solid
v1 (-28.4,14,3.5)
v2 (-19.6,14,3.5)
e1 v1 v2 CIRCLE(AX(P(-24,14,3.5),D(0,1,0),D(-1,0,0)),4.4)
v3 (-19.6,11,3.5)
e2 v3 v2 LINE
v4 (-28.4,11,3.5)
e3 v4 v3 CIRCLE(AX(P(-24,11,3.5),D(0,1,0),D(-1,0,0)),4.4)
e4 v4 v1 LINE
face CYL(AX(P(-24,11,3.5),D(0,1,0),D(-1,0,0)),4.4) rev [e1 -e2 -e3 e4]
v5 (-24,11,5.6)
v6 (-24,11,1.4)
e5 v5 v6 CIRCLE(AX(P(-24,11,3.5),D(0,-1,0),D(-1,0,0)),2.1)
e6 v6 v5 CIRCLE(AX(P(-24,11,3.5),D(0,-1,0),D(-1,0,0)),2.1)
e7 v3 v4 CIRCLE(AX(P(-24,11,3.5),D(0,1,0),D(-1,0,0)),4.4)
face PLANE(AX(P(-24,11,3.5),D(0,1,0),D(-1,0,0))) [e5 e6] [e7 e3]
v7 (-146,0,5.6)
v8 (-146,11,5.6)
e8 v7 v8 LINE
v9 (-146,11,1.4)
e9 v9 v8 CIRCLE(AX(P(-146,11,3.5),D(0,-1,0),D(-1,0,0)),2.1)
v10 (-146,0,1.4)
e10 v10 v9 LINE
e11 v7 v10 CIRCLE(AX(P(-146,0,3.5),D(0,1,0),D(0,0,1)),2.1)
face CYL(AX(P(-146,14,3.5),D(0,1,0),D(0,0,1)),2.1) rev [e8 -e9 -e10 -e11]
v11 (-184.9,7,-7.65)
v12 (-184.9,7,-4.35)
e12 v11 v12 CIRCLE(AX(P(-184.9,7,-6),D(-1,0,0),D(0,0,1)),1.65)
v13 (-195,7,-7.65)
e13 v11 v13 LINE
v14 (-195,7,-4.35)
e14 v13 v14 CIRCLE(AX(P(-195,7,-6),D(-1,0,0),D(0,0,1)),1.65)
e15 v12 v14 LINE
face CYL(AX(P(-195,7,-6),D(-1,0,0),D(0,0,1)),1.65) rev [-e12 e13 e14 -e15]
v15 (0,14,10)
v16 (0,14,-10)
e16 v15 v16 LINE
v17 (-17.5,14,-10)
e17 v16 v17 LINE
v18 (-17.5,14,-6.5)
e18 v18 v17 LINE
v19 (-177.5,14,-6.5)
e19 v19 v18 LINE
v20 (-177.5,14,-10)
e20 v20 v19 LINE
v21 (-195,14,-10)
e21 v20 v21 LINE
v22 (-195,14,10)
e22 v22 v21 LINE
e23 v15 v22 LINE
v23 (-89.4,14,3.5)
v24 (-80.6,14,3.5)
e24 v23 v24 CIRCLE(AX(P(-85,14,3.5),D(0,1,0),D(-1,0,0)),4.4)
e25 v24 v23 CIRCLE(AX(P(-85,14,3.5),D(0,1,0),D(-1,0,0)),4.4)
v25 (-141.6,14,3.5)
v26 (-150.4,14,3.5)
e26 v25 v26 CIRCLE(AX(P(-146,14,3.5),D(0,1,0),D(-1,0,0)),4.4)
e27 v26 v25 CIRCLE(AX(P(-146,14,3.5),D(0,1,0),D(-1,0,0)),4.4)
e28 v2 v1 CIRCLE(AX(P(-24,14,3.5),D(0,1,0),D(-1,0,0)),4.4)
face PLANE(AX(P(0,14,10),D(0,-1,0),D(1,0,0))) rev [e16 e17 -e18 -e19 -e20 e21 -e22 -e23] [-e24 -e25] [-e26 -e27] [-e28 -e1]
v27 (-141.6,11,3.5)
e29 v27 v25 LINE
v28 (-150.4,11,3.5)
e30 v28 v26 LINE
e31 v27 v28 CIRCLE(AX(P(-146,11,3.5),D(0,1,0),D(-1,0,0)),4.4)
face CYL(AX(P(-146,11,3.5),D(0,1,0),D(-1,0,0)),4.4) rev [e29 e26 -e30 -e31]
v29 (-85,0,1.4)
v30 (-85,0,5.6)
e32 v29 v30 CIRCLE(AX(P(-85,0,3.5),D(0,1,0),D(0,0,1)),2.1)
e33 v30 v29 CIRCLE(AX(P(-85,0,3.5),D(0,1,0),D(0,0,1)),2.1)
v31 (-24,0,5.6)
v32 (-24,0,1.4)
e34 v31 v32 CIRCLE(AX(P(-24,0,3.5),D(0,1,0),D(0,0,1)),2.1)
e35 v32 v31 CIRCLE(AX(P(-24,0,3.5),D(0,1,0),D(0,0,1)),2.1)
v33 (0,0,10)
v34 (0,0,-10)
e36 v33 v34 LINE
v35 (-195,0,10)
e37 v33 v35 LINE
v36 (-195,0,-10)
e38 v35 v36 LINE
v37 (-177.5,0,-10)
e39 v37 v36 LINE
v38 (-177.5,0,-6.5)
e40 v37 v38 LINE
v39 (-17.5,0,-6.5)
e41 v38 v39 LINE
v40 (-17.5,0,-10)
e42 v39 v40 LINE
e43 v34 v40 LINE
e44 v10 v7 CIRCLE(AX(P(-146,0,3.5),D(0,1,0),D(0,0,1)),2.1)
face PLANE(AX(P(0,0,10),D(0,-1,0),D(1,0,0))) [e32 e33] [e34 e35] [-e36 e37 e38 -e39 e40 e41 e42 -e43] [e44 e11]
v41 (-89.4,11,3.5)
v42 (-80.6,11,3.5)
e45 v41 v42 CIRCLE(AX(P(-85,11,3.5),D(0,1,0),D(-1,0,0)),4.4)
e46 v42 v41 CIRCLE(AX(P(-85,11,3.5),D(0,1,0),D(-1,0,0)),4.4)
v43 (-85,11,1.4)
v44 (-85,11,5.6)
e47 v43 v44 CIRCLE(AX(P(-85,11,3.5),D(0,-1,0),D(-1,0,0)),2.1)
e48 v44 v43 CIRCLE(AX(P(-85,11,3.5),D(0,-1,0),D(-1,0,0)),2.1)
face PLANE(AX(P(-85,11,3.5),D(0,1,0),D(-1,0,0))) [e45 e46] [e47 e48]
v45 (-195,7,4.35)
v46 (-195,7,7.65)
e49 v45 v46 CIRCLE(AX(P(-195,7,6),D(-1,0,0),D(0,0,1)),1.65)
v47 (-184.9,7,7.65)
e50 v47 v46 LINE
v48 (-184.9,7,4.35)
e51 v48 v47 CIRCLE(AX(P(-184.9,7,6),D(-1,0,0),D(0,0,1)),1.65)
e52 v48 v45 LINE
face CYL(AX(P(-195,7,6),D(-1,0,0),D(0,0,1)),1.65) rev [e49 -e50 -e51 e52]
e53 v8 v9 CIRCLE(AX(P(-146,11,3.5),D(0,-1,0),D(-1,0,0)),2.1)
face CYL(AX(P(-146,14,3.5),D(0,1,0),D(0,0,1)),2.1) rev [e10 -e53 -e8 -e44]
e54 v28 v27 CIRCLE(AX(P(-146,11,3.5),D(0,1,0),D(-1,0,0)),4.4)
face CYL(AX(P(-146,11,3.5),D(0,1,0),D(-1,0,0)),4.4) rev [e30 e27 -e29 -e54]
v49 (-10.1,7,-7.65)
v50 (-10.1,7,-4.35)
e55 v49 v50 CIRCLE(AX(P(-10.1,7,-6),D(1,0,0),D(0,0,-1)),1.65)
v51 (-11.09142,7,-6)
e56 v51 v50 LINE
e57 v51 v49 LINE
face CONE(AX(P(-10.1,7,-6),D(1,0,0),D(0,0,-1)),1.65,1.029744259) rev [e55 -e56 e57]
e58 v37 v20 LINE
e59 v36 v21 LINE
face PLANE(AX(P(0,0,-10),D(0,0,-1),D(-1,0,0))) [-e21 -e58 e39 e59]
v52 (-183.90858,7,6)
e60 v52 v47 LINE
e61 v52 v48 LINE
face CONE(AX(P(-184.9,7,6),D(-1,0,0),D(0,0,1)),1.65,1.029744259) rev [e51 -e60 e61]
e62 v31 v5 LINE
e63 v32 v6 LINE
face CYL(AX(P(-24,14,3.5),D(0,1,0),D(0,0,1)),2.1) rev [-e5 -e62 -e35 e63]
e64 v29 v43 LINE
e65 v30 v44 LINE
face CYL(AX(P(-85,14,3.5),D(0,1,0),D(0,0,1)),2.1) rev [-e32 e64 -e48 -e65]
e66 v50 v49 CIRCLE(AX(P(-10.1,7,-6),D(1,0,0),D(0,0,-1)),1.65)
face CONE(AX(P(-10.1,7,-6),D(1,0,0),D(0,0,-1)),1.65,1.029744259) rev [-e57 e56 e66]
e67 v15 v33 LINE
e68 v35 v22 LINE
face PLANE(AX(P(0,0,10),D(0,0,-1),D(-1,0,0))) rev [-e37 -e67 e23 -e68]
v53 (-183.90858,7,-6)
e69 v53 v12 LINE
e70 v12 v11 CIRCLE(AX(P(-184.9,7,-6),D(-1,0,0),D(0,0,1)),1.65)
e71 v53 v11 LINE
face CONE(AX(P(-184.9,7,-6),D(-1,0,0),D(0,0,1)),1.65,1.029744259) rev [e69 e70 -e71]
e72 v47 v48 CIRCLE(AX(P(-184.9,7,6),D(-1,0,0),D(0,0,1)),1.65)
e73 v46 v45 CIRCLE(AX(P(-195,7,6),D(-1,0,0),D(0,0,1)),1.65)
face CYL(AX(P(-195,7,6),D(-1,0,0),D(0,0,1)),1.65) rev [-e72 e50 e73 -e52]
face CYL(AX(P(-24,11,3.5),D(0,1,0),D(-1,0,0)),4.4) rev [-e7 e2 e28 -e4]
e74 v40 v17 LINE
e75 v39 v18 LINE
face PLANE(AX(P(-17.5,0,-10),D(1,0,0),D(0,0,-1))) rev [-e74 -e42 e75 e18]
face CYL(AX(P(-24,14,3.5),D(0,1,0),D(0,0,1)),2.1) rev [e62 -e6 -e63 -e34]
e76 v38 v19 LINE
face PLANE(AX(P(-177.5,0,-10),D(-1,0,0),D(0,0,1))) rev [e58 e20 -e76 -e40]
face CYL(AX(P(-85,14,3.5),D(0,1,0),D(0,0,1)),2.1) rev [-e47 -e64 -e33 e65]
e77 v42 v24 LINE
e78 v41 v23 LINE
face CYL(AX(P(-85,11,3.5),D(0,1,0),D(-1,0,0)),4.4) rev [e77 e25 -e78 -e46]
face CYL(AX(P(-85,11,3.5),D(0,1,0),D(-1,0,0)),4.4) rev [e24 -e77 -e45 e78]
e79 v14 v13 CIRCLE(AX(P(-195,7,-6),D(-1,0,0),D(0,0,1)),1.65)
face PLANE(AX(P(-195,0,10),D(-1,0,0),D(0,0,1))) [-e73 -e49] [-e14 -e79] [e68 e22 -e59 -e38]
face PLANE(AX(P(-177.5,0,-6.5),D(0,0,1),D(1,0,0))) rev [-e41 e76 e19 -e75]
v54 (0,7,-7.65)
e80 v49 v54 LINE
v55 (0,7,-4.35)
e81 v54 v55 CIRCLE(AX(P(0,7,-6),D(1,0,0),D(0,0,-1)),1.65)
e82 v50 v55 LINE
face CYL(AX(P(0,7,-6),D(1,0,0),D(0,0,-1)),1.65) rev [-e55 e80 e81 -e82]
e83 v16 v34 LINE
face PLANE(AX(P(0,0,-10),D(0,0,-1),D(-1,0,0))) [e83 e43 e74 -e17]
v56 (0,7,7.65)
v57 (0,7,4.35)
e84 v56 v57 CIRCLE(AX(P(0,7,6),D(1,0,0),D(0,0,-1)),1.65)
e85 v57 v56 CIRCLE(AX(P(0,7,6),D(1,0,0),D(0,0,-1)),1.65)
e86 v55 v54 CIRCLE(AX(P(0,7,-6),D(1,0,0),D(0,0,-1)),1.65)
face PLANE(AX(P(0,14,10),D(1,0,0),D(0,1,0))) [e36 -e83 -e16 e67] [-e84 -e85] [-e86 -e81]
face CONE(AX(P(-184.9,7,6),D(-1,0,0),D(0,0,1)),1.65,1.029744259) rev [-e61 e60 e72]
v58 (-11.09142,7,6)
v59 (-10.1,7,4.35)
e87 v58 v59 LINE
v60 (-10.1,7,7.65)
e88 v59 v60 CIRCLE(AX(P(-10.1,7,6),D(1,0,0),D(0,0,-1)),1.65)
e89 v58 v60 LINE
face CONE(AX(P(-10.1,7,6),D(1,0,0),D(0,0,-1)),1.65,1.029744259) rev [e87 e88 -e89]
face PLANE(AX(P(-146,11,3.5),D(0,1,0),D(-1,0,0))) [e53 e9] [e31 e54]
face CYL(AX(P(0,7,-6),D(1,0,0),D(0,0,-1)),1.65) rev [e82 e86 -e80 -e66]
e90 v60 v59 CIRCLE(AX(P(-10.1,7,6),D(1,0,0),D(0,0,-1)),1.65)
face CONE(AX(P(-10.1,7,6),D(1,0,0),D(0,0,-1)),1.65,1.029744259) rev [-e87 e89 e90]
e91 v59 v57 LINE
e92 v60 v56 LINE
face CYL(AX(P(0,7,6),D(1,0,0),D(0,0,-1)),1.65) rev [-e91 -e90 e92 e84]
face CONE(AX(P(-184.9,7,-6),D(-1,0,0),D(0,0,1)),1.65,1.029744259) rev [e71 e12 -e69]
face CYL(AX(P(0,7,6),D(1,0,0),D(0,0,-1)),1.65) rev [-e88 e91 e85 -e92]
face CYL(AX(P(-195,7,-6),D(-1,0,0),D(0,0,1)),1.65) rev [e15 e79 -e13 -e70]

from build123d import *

# Parameters (mm, degrees)
SKETCH1_W             = 195
SKETCH1_H             = 14
EXTRUDE_THIN1_DEPTH   = 10
M4_TAPPED_HOLE1_D     = 3.3
M4_TAPPED_HOLE1_DEPTH = 10.1
M4_TAPPED_HOLE1_TIP   = 0.991420021
M4_TAPPED_HOLE2_D     = 3.3
M4_TAPPED_HOLE2_DEPTH = 10.1
M4_TAPPED_HOLE2_TIP   = 0.991420021
M5_TAPPED_HOLE1_D     = 4.2
SKETCH9_R             = 4.4
CUT_EXTRUDE1_DEPTH    = 3
SKETCH10_W            = 160
SKETCH10_H            = 3.5
CUT_EXTRUDE2_DEPTH    = 196.757503049


with BuildPart() as part:
    # Sketch1 → Extrude-Thin1 (new, symmetric)
    with BuildSketch(Plane.XY):
        with Locations((-97.5, 7)):
            Rectangle(SKETCH1_W, SKETCH1_H)
    extrude(amount=EXTRUDE_THIN1_DEPTH, both=True)

    # M4 Tapped Hole1
    with Locations(Plane.ZY.offset(195)):
        with Locations((-6, 7), (6, 7)):
            Hole(M4_TAPPED_HOLE1_D / 2, depth=M4_TAPPED_HOLE1_DEPTH)
            with Locations((0, 0, -(M4_TAPPED_HOLE1_DEPTH + M4_TAPPED_HOLE1_TIP / 2))):  # 118° drill point
                Cone(0, M4_TAPPED_HOLE1_D / 2, M4_TAPPED_HOLE1_TIP, mode=Mode.SUBTRACT)

    # M4 Tapped Hole2
    with Locations(Plane(origin=(0, 0, 0), x_dir=(0, 0, -1), z_dir=(1, 0, 0))):
        with Locations((-6, 7), (6, 7)):
            Hole(M4_TAPPED_HOLE2_D / 2, depth=M4_TAPPED_HOLE2_DEPTH)
            with Locations((0, 0, -(M4_TAPPED_HOLE2_DEPTH + M4_TAPPED_HOLE2_TIP / 2))):  # 118° drill point
                Cone(0, M4_TAPPED_HOLE2_D / 2, M4_TAPPED_HOLE2_TIP, mode=Mode.SUBTRACT)

    # M5 Tapped Hole1 (through all)
    with Locations(Plane(origin=(0, 14, 0), x_dir=(1, 0, 0), z_dir=(0, 1, 0))):
        with Locations((-146, -3.5), (-85, -3.5), (-24, -3.5)):
            Hole(M5_TAPPED_HOLE1_D / 2)

    # Sketch9 → Cut-Extrude1 (cut)
    with BuildSketch(Plane(origin=(0, 14, 0), x_dir=(1, 0, 0), z_dir=(0, 1, 0))):
        with Locations(Location((-146, -3.5, 0), (0, 0, 180))):
            Circle(SKETCH9_R)
        with Locations(Location((-85, -3.5, 0), (0, 0, 180))):
            Circle(SKETCH9_R)
        with Locations(Location((-24, -3.5, 0), (0, 0, 180))):
            Circle(SKETCH9_R)
    extrude(amount=-CUT_EXTRUDE1_DEPTH, mode=Mode.SUBTRACT)

    # Sketch10 → Cut-Extrude2 (cut, through all)
    with BuildSketch(Plane(origin=(0, 14, 0), x_dir=(1, 0, 0), z_dir=(0, 1, 0))):
        with Locations((-97.5, 8.25)):
            Rectangle(SKETCH10_W, SKETCH10_H)
    extrude(amount=-CUT_EXTRUDE2_DEPTH, mode=Mode.SUBTRACT)


solid = part.part
